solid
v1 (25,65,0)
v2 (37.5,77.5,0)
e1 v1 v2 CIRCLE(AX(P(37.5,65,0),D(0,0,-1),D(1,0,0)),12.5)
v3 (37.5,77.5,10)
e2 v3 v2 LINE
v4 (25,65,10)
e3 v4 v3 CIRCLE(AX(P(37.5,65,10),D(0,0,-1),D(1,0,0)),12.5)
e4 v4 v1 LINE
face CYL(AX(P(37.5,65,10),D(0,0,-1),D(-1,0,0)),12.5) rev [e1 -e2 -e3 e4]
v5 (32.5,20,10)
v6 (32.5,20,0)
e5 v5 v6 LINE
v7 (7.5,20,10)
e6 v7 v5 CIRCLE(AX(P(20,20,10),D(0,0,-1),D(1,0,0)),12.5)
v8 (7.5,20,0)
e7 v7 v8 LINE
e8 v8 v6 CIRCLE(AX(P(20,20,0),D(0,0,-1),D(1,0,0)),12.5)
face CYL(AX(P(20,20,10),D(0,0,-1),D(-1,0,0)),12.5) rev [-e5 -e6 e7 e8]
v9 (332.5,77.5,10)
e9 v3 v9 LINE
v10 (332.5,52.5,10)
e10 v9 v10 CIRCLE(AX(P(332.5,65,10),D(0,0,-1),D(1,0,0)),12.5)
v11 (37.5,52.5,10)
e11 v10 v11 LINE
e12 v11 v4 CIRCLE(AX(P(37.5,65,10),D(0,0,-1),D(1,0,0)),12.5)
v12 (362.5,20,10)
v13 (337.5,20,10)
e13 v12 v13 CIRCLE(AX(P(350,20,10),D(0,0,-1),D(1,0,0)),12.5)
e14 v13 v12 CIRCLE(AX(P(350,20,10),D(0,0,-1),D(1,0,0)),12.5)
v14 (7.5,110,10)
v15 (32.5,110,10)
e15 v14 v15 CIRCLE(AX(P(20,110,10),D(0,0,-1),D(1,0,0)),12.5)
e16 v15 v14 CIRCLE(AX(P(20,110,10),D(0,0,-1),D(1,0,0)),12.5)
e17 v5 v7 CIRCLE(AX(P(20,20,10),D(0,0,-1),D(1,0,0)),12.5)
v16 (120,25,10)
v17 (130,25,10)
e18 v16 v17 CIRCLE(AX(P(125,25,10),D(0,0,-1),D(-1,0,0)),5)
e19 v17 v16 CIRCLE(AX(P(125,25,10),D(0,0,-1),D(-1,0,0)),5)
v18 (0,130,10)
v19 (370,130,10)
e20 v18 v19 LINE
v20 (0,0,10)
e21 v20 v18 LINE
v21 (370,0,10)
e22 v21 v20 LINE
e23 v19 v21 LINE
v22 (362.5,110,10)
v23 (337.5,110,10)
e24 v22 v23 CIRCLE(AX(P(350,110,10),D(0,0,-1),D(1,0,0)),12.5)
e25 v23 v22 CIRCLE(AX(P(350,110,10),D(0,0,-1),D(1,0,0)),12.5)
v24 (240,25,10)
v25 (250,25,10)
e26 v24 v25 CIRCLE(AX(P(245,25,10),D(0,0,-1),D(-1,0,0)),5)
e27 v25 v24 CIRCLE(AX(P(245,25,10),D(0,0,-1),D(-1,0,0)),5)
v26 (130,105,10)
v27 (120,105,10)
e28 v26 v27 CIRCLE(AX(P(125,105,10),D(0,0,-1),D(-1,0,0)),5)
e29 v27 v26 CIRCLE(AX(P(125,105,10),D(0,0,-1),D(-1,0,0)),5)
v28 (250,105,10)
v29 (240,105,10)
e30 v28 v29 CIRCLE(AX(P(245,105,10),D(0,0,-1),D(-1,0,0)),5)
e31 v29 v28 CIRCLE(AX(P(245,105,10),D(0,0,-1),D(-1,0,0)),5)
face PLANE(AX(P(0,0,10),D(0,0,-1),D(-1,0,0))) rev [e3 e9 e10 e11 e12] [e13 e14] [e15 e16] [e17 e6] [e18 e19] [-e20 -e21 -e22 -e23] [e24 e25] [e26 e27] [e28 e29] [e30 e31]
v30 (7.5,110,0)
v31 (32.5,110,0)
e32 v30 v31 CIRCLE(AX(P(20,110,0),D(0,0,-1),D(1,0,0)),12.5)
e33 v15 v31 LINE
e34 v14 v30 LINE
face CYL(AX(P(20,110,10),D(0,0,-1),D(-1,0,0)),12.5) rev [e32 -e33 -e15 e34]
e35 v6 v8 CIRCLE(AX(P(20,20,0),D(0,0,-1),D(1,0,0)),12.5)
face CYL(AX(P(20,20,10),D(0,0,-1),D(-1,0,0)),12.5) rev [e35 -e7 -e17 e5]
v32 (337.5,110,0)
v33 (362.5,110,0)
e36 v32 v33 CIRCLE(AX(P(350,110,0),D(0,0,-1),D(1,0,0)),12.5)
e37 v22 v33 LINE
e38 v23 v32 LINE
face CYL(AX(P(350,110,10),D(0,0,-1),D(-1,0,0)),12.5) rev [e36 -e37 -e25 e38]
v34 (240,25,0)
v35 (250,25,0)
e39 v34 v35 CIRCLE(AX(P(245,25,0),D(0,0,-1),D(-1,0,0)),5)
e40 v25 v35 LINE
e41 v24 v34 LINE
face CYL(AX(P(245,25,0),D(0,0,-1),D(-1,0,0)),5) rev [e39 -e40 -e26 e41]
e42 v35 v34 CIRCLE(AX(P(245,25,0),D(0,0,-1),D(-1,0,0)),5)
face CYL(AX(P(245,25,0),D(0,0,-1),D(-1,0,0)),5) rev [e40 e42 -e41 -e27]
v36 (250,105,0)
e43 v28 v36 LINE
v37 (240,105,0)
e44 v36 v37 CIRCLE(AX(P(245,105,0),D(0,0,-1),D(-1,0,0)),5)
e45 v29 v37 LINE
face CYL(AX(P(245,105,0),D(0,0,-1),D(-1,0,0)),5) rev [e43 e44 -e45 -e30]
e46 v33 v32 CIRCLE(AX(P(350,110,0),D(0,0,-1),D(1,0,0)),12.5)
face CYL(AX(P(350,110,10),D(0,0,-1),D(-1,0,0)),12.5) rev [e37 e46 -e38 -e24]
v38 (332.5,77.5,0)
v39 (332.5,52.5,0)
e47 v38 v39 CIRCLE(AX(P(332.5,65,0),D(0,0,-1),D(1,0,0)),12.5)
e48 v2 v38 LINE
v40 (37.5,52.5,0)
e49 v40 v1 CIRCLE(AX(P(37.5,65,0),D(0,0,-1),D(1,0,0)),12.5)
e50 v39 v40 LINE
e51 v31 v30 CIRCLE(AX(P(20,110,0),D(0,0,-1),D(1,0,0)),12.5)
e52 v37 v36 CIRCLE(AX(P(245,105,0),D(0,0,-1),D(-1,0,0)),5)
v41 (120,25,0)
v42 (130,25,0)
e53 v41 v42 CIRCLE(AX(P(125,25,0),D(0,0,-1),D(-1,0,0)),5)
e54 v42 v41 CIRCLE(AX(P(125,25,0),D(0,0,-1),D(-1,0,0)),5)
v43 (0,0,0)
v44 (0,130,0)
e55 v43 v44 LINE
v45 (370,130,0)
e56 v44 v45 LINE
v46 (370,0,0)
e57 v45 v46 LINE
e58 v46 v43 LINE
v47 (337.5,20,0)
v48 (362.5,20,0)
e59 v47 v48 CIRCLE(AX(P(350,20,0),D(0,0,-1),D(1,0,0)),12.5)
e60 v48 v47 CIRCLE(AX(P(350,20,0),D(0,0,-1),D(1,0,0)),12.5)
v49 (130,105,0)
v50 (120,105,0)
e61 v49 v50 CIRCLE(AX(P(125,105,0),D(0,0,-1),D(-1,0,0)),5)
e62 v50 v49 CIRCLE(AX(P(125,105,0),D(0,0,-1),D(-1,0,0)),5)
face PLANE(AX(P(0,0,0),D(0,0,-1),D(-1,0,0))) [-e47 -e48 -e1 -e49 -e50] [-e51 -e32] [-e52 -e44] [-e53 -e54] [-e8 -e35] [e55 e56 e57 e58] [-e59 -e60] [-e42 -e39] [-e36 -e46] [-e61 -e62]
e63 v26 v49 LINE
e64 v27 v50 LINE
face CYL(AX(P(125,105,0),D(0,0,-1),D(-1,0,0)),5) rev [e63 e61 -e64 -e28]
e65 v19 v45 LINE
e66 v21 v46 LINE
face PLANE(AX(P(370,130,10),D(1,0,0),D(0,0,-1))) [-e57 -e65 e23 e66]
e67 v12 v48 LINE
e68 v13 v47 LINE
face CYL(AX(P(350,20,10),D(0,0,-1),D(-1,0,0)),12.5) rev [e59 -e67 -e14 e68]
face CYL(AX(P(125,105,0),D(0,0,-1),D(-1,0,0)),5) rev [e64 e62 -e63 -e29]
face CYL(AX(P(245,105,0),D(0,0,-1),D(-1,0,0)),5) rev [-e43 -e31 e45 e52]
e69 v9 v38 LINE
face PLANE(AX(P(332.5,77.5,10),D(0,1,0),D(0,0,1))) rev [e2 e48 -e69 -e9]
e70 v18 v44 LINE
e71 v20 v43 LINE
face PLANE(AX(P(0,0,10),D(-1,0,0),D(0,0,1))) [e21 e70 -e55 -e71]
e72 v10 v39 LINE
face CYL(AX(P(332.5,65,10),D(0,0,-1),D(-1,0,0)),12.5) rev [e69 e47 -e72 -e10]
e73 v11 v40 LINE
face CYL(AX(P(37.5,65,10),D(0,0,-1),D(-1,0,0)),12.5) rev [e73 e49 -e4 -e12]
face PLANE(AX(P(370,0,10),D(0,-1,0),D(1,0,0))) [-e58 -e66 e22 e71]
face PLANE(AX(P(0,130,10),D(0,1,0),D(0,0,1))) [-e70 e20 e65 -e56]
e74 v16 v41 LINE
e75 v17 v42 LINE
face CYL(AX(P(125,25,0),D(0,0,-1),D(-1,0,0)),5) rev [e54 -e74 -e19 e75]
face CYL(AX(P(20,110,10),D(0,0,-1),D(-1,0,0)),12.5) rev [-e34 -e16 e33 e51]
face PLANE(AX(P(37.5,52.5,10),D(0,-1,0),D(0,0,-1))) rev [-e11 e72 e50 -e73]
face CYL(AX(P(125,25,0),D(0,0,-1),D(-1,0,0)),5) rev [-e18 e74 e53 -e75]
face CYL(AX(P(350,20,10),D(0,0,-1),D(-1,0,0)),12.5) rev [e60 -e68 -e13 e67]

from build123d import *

# Parameters (mm, degrees)
SKETCH1_W            = 370
SKETCH1_H            = 130
SKETCH1_R            = 12.5
BOSS_EXTRUDE1_DEPTH  = 10
M8_CLEARANCE_HOLE1_D = 10


with BuildPart() as part:
    # Sketch1 → Boss-Extrude1 (new body)
    with BuildSketch(Plane(origin=(0, 0, 0), x_dir=(-1, 0, 0), z_dir=(0, 0, -1))):
        with Locations((-185, 65)):
            Rectangle(SKETCH1_W, SKETCH1_H)
        with Locations(Location((-350, 20, 0), (0, 0, 180))):
            Circle(SKETCH1_R, mode=Mode.SUBTRACT)
        with Locations(Location((-20, 110, 0), (0, 0, 180))):
            Circle(SKETCH1_R, mode=Mode.SUBTRACT)
        with Locations(Location((-350, 110, 0), (0, 0, 180))):
            Circle(SKETCH1_R, mode=Mode.SUBTRACT)
        with Locations(Location((-20, 20, 0), (0, 0, 180))):
            Circle(SKETCH1_R, mode=Mode.SUBTRACT)
        with BuildLine():
            Line((-37.5, 52.5), (-332.5, 52.5))
            ThreePointArc((-332.5, 52.5), (-345, 65), (-332.5, 77.5))
            Line((-332.5, 77.5), (-37.5, 77.5))
            ThreePointArc((-37.5, 77.5), (-25, 65), (-37.5, 52.5))
        make_face(mode=Mode.SUBTRACT)
    extrude(amount=-BOSS_EXTRUDE1_DEPTH)

    # M8 Clearance Hole1 (through all)
    with Locations(Plane(origin=(0, 0, 0), x_dir=(-1, 0, 0), z_dir=(0, 0, -1))):
        with Locations((-245, 25), (-125, 25), (-125, 105), (-245, 105)):
            Hole(M8_CLEARANCE_HOLE1_D / 2)


solid = part.part
